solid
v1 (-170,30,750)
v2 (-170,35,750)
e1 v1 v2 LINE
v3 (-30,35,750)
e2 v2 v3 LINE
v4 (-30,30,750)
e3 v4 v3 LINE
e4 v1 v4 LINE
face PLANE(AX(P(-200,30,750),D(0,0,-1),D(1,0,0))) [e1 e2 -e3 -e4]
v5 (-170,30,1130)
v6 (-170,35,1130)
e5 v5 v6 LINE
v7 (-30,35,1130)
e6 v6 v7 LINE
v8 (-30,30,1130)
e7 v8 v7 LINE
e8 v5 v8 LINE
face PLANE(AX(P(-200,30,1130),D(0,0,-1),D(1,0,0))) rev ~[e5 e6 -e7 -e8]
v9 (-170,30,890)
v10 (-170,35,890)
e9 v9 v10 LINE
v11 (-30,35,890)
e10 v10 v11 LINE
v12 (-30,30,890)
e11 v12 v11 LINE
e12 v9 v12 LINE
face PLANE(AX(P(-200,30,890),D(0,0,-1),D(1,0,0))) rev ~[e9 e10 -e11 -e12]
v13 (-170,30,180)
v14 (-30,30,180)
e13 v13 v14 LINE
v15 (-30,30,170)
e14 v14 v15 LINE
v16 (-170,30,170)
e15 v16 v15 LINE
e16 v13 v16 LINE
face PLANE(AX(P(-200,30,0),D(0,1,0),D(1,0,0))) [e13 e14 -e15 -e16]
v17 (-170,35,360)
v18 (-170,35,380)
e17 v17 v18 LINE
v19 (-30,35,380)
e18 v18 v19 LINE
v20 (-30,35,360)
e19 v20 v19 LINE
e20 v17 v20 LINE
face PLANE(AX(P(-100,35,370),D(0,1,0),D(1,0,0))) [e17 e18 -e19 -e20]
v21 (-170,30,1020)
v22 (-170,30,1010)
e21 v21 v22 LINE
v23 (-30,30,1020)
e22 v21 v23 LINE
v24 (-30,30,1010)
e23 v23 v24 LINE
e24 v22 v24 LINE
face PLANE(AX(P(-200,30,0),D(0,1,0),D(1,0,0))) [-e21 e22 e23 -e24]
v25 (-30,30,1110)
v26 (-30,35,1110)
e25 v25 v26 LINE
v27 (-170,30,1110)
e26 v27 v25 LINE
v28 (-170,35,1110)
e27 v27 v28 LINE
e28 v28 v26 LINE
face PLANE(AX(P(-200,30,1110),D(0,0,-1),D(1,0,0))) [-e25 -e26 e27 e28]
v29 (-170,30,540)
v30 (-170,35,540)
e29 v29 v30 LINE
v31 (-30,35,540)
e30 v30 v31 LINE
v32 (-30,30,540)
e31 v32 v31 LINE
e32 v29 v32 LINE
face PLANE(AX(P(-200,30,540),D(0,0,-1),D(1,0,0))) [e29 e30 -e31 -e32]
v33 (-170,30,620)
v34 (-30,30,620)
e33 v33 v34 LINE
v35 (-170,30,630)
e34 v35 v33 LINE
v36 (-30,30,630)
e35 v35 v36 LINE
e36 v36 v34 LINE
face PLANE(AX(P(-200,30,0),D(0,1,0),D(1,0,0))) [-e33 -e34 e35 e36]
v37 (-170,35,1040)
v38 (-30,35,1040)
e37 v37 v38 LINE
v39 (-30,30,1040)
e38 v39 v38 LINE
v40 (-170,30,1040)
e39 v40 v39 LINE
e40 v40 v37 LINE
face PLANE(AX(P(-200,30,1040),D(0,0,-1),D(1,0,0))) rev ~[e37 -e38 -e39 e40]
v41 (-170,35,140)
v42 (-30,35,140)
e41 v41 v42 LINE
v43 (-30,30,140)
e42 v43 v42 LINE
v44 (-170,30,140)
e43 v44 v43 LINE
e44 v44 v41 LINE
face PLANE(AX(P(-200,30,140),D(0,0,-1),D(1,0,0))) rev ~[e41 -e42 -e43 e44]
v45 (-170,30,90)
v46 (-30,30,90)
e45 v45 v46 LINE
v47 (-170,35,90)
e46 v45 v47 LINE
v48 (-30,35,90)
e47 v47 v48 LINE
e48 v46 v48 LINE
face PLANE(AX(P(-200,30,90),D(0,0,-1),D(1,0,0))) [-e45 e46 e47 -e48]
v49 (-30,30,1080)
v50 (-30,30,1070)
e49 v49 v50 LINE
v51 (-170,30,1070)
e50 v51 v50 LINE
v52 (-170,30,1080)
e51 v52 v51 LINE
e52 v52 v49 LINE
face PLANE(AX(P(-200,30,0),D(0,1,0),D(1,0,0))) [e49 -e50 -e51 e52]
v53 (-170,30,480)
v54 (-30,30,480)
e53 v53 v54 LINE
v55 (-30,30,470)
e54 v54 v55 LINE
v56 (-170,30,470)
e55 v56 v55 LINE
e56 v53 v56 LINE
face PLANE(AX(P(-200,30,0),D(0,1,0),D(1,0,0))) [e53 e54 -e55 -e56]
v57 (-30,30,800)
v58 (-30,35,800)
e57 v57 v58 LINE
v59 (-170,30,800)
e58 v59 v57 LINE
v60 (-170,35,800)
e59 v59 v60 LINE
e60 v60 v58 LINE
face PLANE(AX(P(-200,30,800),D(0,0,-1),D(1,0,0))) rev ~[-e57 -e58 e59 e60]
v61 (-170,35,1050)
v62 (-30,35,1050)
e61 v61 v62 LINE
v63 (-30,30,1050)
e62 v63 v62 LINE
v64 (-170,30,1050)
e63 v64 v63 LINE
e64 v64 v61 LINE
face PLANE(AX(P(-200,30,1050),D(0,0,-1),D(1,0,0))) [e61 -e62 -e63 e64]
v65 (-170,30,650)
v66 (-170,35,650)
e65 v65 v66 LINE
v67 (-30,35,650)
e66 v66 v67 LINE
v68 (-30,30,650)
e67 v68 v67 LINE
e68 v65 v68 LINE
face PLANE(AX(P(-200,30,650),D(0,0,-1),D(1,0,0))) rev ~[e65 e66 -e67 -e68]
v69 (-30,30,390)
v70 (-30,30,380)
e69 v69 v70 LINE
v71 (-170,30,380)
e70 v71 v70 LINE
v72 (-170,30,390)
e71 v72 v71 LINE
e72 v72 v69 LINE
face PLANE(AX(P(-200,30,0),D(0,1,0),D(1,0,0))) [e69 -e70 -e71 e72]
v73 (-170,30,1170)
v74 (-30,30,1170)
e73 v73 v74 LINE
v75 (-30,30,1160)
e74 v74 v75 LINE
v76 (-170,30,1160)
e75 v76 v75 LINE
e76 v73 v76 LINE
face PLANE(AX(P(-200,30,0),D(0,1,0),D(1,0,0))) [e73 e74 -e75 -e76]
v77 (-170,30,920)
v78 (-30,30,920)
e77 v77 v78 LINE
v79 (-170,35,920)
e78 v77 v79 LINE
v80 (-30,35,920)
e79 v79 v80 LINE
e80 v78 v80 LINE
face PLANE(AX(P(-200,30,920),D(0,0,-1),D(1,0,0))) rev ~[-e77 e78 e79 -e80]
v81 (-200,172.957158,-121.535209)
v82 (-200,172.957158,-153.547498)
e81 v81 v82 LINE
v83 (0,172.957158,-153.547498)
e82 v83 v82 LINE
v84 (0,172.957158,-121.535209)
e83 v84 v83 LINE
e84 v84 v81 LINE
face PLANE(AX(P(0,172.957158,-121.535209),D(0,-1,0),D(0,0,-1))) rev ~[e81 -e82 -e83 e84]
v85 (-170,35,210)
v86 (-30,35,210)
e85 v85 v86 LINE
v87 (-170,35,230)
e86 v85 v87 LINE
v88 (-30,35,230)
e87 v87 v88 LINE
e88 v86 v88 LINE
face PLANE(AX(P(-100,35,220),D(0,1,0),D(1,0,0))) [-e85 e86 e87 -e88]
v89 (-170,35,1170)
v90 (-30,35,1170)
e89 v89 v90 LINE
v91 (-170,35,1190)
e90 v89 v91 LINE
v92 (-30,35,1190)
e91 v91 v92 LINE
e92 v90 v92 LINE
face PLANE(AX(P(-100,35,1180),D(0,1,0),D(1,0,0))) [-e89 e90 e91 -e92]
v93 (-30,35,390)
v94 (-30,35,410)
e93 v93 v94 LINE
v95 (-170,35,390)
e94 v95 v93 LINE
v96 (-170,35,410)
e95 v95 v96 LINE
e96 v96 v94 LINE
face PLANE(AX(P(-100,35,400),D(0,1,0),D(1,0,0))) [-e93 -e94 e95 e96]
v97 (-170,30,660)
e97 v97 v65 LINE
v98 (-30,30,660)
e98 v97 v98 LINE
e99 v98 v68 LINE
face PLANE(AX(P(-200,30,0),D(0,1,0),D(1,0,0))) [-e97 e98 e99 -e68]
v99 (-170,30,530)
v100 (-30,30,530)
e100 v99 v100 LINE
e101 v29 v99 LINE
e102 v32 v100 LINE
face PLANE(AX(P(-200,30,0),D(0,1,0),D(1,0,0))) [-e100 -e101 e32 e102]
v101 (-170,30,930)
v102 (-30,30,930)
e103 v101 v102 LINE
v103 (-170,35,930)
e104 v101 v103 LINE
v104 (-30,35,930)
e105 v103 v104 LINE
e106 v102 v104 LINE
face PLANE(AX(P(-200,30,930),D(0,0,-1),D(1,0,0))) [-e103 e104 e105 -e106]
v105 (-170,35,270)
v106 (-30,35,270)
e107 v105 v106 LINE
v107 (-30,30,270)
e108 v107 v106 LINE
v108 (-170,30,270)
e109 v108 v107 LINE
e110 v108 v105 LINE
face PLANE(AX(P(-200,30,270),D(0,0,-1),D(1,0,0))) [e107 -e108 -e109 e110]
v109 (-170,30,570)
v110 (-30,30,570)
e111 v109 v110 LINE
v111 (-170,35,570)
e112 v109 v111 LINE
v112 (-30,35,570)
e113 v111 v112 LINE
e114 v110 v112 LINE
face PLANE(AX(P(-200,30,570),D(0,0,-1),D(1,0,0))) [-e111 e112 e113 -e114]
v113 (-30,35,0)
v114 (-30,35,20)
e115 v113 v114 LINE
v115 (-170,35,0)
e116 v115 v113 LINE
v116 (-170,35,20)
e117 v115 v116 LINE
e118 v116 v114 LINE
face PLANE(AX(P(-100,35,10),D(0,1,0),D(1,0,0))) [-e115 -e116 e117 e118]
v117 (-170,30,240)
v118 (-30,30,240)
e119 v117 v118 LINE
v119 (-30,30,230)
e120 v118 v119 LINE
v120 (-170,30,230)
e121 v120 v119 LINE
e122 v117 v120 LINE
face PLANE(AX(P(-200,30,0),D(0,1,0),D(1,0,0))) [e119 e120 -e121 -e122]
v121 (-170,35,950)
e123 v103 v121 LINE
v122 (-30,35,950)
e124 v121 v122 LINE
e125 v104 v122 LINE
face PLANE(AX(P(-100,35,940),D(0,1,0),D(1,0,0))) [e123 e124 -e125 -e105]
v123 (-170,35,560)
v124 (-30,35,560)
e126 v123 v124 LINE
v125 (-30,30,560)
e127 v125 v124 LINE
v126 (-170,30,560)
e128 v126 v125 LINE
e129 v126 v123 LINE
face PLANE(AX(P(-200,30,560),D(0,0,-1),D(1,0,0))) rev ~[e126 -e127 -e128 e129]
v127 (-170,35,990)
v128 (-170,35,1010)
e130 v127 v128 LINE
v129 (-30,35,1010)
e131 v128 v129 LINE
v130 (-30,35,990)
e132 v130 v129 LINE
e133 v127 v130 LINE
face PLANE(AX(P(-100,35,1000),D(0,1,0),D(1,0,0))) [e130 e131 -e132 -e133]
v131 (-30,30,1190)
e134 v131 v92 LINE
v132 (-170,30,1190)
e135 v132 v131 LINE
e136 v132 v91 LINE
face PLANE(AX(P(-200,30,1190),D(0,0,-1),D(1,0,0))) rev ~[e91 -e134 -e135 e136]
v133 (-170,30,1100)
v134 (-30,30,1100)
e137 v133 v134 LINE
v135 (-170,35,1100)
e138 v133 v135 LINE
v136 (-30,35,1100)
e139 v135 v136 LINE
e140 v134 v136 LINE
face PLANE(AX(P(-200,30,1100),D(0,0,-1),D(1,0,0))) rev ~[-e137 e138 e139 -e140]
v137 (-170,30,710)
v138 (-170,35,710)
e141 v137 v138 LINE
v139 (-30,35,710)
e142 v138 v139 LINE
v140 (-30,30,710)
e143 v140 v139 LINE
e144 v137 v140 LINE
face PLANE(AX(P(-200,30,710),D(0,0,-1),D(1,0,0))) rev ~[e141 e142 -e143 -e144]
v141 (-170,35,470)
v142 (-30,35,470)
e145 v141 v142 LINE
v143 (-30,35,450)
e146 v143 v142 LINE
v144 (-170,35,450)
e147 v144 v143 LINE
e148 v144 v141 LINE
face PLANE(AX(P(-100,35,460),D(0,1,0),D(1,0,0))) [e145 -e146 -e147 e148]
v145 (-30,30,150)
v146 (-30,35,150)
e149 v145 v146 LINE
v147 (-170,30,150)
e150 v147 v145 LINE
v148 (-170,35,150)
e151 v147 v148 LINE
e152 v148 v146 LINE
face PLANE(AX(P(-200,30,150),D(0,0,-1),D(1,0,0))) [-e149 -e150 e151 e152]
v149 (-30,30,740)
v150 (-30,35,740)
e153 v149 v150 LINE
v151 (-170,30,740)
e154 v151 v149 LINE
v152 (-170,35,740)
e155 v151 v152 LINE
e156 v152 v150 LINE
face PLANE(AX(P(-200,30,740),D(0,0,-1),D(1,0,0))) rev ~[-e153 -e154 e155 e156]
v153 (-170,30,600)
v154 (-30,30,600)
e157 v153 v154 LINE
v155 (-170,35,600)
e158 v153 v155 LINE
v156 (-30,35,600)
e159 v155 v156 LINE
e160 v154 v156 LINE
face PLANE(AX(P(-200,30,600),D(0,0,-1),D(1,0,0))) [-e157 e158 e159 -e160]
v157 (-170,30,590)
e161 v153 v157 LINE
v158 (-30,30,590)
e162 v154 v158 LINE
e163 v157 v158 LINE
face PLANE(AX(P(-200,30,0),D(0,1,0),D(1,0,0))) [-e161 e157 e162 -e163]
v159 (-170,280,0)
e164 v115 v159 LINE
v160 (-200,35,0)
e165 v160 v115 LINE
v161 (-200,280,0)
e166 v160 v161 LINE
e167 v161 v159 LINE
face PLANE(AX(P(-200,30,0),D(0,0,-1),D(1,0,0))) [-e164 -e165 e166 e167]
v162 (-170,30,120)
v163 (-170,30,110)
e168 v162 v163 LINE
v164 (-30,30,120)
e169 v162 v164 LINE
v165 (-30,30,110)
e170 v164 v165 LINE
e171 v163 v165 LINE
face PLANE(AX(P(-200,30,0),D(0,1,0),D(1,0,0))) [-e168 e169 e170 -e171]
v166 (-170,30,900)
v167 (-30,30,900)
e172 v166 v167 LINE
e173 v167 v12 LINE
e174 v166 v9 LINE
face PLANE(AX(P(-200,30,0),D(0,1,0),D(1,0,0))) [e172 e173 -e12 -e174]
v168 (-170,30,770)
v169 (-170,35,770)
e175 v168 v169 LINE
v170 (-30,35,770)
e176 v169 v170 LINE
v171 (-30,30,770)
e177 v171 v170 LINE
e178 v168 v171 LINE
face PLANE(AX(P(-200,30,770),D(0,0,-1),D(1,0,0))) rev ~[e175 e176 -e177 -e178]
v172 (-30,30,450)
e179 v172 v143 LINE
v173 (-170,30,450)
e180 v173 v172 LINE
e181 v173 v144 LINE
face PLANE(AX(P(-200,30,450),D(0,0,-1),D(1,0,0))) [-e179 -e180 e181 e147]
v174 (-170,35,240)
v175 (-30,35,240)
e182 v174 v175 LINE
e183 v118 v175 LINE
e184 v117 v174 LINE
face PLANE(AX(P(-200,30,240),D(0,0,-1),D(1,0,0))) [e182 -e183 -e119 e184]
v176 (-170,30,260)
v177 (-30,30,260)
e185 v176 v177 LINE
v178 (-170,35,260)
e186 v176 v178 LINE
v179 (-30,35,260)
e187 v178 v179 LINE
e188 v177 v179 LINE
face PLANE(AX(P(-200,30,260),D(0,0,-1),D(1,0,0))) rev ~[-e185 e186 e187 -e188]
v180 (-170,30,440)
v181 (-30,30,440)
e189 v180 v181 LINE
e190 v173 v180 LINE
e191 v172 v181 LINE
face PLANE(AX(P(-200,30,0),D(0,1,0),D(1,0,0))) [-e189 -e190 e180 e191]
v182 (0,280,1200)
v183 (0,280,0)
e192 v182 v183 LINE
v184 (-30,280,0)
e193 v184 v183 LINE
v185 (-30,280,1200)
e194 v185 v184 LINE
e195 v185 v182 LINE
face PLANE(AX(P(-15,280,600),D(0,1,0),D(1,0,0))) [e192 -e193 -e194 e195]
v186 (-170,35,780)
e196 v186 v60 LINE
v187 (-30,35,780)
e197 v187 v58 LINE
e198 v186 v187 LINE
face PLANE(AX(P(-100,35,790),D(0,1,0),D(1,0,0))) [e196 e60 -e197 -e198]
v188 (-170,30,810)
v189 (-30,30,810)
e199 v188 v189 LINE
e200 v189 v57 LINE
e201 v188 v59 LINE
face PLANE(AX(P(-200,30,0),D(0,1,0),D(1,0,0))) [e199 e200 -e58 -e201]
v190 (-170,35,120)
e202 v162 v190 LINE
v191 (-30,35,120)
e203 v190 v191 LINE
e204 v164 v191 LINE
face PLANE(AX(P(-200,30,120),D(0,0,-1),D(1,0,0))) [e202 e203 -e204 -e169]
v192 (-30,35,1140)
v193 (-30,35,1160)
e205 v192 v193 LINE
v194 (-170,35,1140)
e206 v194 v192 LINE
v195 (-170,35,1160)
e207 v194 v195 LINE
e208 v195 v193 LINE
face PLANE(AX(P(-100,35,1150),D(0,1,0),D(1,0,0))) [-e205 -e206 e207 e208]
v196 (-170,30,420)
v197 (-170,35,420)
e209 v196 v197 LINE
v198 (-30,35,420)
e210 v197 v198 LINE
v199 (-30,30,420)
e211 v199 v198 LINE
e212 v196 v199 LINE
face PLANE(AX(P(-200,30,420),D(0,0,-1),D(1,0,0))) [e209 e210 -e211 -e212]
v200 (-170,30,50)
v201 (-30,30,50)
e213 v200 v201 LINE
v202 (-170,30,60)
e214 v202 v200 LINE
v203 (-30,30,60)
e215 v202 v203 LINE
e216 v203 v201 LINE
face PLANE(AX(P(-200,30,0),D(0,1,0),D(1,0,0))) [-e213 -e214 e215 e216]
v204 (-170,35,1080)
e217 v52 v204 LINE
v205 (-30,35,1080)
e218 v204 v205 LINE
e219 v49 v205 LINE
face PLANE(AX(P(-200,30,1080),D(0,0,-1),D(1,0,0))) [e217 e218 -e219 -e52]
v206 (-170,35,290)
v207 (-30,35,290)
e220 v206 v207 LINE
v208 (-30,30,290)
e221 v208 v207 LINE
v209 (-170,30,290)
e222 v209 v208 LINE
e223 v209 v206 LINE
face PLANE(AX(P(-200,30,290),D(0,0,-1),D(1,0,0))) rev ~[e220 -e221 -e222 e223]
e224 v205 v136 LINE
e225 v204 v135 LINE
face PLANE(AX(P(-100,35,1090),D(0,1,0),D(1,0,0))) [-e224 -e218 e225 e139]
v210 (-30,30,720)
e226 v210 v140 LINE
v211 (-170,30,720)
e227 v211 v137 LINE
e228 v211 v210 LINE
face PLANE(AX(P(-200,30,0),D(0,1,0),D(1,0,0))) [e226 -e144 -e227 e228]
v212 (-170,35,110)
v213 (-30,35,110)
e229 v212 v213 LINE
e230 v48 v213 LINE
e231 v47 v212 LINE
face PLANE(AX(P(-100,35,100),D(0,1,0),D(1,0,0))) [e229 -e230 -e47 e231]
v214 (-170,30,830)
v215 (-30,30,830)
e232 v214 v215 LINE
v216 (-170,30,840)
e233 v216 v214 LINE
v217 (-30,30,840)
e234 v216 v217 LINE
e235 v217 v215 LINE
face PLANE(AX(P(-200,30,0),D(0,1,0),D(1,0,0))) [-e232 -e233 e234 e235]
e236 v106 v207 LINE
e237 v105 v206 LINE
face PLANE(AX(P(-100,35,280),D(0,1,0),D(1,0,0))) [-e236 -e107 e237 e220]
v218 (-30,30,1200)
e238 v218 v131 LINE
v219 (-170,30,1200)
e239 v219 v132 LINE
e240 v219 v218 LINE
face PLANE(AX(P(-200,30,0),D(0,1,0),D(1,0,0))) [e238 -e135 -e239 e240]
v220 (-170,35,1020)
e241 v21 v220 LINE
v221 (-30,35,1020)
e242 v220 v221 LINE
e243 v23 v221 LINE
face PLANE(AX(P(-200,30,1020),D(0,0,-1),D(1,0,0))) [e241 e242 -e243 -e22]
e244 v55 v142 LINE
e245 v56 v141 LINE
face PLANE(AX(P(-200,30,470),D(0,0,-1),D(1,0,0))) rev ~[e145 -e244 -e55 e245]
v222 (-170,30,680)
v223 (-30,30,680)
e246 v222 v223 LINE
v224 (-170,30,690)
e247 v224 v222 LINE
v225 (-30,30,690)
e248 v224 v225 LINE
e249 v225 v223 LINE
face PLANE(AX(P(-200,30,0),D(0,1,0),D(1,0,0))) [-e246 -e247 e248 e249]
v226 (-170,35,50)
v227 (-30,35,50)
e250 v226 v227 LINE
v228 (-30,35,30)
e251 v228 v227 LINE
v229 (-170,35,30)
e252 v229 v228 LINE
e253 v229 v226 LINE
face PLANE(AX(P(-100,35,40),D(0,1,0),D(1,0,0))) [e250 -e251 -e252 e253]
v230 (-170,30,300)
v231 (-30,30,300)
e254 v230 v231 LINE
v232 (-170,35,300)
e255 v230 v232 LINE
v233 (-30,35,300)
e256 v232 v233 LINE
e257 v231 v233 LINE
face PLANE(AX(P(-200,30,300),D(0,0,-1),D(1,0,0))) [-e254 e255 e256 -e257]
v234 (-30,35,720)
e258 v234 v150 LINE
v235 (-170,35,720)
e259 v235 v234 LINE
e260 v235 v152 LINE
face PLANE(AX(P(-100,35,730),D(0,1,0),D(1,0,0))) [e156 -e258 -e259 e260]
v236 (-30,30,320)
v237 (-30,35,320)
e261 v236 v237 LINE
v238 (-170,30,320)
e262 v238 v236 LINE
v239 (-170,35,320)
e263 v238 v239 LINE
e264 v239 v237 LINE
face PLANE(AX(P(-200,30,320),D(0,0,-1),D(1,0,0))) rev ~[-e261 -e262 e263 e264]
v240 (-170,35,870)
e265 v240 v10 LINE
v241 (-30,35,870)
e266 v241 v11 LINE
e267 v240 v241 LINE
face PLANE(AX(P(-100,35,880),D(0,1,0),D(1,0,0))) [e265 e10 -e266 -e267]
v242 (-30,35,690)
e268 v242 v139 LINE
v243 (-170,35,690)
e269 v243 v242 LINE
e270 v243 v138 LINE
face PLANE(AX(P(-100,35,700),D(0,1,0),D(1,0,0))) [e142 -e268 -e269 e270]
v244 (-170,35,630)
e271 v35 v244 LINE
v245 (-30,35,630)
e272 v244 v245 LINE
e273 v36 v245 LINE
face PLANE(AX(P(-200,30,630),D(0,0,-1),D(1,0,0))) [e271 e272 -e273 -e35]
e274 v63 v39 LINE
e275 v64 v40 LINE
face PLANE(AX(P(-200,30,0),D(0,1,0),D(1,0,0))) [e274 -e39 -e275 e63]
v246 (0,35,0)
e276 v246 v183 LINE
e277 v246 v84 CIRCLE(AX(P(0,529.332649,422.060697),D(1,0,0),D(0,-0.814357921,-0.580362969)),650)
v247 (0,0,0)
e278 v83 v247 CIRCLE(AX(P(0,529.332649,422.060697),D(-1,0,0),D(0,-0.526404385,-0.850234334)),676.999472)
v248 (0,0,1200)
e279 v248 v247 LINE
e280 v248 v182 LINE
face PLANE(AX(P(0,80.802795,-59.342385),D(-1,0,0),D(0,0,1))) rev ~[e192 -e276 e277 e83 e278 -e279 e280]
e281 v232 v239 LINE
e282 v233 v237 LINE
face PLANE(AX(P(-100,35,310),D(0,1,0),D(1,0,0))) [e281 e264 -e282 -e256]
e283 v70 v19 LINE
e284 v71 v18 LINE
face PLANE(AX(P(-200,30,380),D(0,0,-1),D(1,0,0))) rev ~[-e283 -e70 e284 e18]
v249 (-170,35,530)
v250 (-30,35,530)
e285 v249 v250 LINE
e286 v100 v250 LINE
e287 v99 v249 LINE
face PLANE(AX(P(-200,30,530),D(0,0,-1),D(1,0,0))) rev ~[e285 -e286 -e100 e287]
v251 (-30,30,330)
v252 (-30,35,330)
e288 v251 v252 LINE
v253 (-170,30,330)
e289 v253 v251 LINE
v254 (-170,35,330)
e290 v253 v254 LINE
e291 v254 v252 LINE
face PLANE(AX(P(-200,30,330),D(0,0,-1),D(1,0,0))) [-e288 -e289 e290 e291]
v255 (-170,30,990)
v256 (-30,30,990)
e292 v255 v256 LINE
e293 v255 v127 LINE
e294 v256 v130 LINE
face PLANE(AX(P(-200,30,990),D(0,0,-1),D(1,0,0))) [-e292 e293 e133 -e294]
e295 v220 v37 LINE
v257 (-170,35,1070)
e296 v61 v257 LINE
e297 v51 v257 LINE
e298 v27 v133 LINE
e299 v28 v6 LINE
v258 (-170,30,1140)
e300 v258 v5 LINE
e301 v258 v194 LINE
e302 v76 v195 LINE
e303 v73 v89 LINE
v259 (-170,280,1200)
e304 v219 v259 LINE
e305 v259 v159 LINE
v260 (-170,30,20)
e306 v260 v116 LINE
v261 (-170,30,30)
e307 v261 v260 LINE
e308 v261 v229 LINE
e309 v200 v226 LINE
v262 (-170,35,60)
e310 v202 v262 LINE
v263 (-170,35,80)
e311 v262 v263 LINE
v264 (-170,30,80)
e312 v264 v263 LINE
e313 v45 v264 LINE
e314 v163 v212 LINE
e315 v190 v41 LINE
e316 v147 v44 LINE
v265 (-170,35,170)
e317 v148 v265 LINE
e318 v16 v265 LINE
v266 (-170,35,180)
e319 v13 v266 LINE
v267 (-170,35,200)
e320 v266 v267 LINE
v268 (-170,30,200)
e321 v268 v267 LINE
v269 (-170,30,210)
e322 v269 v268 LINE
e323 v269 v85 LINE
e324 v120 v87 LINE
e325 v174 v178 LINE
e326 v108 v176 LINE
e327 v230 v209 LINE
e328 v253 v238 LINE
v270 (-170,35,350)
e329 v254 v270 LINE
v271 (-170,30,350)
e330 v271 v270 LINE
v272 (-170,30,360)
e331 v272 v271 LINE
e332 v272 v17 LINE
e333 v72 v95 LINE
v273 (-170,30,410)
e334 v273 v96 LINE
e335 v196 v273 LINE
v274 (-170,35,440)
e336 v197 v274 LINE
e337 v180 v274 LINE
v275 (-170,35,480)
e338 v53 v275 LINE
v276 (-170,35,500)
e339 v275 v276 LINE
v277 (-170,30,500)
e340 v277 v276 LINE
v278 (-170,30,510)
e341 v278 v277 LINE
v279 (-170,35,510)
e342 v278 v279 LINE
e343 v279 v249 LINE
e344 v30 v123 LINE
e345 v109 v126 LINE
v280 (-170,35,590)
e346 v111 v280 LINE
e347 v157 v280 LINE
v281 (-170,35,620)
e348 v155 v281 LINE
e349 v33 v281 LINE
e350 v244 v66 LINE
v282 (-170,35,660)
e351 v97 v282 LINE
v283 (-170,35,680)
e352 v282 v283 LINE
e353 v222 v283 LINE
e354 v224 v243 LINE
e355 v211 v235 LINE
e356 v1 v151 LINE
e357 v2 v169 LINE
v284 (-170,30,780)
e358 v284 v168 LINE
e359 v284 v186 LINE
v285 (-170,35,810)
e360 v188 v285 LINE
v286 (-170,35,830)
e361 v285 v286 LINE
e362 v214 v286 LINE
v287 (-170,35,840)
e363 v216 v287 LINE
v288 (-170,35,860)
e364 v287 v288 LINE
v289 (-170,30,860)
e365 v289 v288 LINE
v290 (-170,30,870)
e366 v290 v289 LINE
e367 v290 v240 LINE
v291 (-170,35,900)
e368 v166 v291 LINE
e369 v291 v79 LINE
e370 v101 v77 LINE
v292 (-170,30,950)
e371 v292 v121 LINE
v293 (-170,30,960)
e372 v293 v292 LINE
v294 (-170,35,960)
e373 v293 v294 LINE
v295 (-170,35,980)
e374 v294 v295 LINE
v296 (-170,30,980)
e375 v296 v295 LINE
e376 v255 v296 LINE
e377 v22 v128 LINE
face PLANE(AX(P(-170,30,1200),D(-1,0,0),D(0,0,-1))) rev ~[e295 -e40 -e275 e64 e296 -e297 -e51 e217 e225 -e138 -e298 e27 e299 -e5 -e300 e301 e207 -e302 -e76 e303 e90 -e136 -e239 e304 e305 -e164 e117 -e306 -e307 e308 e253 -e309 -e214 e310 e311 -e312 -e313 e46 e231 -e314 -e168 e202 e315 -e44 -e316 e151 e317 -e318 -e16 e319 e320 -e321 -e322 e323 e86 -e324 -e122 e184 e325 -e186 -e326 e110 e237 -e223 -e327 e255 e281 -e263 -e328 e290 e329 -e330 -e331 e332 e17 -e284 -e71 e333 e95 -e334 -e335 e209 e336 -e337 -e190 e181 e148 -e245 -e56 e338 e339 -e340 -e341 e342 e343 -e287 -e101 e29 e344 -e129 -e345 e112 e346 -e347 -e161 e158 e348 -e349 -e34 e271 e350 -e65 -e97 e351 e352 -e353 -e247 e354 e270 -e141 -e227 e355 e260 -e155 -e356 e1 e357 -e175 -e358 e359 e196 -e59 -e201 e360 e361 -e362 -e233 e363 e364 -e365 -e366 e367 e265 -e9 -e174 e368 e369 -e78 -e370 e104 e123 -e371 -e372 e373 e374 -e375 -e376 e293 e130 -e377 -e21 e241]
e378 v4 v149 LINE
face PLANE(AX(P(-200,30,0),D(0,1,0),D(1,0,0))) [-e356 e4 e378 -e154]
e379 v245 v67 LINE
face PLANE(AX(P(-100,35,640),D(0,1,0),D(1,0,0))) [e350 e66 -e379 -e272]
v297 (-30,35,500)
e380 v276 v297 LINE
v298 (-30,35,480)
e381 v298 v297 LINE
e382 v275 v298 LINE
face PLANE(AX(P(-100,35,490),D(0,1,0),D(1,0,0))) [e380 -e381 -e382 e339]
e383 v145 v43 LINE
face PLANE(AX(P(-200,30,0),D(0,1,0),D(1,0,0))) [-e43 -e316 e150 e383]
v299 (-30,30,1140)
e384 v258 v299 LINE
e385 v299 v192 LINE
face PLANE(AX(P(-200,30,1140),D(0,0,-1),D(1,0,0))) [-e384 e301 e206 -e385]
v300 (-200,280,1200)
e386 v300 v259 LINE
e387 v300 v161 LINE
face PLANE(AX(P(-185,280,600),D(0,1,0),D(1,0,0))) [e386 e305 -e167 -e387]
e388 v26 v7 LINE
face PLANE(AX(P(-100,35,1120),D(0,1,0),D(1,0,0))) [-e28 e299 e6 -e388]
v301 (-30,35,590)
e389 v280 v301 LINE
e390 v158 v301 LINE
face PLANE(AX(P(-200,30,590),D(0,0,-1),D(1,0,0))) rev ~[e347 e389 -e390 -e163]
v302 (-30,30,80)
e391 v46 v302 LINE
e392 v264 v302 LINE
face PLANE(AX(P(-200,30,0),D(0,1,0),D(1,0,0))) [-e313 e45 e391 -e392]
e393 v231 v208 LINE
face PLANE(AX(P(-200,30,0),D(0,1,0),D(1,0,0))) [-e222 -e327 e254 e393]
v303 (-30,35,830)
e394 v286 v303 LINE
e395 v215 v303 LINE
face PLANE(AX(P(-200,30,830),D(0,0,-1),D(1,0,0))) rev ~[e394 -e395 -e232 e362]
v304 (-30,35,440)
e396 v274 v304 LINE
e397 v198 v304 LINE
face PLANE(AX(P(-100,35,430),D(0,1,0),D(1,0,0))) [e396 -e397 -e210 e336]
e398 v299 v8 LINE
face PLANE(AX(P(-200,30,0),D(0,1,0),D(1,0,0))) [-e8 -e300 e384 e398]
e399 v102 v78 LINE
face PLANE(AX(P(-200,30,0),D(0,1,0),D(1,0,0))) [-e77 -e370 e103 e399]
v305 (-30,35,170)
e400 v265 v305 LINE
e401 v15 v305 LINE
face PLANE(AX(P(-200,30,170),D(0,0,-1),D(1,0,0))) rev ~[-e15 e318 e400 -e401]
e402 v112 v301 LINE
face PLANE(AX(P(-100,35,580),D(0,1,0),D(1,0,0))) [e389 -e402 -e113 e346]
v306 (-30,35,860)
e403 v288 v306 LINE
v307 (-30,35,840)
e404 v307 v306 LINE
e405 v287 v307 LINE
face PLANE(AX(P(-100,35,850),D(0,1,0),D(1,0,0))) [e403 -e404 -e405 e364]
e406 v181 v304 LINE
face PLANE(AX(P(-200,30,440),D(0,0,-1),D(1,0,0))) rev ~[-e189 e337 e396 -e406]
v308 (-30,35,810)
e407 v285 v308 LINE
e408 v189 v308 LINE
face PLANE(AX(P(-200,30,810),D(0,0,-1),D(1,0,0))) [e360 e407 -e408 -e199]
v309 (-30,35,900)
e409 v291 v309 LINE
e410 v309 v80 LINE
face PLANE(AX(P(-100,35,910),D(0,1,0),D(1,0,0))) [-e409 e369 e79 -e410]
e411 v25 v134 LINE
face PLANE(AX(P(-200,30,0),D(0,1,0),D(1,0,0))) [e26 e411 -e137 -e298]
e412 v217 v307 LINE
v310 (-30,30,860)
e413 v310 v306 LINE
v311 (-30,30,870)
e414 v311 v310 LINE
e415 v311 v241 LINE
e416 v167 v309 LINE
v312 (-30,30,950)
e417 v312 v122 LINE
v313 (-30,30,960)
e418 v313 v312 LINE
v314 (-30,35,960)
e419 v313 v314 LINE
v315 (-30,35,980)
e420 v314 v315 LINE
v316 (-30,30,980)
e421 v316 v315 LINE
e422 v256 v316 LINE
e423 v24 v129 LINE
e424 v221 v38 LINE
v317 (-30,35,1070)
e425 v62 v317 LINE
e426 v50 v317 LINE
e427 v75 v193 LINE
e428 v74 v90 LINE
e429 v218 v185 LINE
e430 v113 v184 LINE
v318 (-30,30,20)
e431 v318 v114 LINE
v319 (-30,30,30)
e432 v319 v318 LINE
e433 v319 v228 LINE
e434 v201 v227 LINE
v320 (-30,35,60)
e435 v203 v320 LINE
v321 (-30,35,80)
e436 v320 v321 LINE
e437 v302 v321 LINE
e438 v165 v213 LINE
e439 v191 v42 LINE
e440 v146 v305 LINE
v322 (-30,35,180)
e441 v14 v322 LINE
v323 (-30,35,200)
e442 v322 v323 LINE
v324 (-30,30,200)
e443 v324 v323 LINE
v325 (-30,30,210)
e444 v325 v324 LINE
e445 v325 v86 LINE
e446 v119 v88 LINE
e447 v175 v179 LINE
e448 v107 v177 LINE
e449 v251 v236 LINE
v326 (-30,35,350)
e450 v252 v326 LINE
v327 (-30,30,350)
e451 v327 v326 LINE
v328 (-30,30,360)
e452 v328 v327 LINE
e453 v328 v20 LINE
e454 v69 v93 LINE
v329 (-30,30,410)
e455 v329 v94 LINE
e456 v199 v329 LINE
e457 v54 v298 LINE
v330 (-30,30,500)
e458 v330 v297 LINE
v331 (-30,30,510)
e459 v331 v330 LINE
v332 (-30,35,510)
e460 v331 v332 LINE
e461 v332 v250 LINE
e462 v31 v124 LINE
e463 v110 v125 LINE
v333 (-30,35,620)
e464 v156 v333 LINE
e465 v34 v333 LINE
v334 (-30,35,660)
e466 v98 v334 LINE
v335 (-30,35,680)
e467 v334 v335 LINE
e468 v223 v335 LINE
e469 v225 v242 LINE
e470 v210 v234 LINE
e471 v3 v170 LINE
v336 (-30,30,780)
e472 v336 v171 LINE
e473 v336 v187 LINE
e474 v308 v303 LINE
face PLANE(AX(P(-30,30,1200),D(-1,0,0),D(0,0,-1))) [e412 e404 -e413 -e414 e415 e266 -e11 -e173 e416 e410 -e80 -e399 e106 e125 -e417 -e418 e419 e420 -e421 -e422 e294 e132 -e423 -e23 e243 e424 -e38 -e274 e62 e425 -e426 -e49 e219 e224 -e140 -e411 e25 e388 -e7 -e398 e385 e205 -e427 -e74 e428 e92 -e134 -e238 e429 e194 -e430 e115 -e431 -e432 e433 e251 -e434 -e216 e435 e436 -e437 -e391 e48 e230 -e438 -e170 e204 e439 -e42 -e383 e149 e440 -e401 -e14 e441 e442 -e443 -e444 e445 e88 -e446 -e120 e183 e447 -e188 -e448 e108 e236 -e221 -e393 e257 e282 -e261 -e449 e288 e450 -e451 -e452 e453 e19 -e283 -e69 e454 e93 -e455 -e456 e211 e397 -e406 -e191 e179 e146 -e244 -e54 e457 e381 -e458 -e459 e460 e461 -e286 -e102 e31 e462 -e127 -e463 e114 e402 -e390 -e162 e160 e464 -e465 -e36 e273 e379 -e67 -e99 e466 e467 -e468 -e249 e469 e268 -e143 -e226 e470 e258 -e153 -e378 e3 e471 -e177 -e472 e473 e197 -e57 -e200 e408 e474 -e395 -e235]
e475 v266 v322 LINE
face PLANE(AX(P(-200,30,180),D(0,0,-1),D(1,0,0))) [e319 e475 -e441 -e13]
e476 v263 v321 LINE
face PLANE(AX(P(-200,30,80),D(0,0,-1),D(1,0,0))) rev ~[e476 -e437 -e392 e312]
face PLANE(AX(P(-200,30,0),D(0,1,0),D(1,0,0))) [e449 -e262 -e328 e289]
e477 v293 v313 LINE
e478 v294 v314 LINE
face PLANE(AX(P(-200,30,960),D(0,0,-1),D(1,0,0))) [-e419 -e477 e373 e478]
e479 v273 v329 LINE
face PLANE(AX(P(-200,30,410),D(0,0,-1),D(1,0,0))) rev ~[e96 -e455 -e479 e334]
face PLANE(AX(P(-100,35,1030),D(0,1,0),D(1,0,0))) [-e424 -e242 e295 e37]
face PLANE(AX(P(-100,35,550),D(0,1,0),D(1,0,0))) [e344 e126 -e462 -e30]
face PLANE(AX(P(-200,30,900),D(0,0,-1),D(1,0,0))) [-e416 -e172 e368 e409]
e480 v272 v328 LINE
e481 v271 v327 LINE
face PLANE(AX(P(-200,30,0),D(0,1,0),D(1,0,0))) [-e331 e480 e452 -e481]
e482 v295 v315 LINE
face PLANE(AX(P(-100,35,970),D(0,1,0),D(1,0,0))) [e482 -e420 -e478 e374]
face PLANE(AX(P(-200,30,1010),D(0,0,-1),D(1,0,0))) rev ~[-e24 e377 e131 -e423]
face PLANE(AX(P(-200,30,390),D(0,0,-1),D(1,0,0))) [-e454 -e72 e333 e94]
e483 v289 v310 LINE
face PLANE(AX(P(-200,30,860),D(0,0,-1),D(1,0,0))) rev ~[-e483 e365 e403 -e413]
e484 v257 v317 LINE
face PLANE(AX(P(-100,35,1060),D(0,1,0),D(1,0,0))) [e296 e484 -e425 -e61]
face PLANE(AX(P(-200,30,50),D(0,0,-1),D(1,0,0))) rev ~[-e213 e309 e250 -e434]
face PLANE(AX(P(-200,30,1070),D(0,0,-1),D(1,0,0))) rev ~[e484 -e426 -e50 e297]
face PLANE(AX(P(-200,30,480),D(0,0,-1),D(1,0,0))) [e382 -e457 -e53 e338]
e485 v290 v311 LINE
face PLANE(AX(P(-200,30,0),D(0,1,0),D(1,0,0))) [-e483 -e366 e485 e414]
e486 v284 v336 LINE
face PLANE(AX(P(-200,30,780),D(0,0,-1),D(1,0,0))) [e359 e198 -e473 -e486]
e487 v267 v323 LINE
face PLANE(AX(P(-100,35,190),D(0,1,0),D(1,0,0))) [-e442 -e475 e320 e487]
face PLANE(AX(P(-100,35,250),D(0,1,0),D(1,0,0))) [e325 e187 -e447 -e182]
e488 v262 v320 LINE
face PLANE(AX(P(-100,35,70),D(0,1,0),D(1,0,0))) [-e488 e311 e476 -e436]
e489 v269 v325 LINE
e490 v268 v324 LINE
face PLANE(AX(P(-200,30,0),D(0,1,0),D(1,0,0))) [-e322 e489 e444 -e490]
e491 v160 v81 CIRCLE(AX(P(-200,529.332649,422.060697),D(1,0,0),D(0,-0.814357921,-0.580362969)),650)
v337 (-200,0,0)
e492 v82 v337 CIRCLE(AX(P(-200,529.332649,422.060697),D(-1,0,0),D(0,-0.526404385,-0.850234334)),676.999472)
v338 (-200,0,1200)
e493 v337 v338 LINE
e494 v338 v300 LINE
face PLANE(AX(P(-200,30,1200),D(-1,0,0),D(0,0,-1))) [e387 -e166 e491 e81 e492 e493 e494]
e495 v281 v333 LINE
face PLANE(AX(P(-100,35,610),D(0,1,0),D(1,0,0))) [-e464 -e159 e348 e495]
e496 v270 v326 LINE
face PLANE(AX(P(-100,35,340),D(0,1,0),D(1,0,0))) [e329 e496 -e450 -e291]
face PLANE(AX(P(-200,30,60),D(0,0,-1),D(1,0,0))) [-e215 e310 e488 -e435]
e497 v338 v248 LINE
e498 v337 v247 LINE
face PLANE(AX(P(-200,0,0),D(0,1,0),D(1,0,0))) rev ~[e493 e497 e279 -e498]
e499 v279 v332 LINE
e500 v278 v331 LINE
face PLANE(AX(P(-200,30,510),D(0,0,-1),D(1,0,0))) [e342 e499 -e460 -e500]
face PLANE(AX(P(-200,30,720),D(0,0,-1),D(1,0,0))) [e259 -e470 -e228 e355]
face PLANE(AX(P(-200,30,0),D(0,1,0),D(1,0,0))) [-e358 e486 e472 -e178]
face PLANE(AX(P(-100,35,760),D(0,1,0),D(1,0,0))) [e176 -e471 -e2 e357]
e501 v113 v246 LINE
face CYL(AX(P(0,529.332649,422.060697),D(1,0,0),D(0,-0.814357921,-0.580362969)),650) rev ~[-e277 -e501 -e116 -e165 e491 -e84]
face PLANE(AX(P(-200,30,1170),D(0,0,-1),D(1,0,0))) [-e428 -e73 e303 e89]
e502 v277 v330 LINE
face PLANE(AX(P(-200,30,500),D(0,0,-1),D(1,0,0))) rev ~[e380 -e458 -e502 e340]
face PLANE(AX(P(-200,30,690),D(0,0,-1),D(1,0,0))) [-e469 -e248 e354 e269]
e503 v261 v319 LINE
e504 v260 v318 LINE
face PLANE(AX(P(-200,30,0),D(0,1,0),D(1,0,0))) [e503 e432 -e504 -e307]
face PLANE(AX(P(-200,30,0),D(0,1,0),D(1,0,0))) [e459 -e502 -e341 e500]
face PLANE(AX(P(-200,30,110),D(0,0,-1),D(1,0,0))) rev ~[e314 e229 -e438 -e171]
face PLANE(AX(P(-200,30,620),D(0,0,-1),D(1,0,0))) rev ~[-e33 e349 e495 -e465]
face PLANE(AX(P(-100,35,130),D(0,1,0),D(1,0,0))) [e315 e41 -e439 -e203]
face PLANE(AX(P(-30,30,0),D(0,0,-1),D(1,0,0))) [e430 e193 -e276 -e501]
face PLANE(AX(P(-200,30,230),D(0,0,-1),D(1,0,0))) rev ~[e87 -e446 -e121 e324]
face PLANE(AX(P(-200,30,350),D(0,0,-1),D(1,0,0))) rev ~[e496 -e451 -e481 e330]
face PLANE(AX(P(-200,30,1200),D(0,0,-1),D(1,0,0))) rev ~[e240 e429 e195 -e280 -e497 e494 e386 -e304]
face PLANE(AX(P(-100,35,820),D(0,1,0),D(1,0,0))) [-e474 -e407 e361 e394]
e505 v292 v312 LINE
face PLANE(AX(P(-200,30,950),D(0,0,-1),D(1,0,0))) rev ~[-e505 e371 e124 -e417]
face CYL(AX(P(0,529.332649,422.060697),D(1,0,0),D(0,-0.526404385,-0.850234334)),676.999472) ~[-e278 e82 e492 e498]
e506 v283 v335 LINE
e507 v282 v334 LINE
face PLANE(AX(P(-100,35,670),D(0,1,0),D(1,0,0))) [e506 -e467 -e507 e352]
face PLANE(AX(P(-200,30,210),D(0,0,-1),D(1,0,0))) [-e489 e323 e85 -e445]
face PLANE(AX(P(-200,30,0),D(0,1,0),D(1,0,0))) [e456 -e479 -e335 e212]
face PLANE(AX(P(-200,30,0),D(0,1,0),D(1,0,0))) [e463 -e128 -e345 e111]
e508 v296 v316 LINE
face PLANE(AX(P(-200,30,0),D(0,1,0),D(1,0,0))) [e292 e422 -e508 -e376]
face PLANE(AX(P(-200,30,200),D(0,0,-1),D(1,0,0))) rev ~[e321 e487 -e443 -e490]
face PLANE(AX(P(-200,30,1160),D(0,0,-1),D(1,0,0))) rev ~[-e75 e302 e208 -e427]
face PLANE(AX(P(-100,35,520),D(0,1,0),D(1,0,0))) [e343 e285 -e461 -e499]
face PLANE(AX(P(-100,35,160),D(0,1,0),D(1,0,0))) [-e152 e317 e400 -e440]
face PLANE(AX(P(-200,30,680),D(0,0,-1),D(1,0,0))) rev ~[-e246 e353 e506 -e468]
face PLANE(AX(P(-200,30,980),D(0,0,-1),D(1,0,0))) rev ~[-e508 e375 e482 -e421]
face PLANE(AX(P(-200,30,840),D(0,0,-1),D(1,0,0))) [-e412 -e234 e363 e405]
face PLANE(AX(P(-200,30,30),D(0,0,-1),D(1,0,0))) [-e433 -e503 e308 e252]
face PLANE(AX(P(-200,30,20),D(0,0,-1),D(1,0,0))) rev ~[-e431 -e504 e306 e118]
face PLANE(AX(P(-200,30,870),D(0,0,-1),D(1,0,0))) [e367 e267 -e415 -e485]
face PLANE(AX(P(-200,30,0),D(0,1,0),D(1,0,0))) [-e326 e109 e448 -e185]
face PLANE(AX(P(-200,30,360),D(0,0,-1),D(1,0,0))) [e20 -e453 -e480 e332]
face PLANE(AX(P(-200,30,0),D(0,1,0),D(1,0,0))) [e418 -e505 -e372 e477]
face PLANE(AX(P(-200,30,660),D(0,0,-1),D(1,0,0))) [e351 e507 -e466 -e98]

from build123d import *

# Parameters (mm, degrees)
SKETCH1_W           = 200
SKETCH1_H           = 30
BOSS_EXTRUDE1_DEPTH = 1200
SKETCH2_W           = 200
SKETCH2_H           = 20
BOSS_EXTRUDE2_DEPTH = 5
BOSS_EXTRUDE3_DEPTH = 200
SKETCH5_W           = 30
SKETCH5_H           = 1200
BOSS_EXTRUDE5_DEPTH = 250


with BuildPart() as part:
    # Sketch1 → Boss-Extrude1 (new body)
    with BuildSketch(Plane.XY):
        with Locations((-100, 15)):
            Rectangle(SKETCH1_W, SKETCH1_H)
    extrude(amount=BOSS_EXTRUDE1_DEPTH)

    # Sketch2 → Boss-Extrude2 (add)
    with BuildSketch(Plane(origin=(0, 30, 0), x_dir=(1, 0, 0), z_dir=(0, 1, 0))):
        with Locations((-100, -10)):
            Rectangle(SKETCH2_W, SKETCH2_H)
        with Locations((-100, -40)):
            Rectangle(SKETCH2_W, SKETCH2_H)
        with Locations((-100, -70)):
            Rectangle(SKETCH2_W, SKETCH2_H)
        with Locations((-100, -100)):
            Rectangle(SKETCH2_W, SKETCH2_H)
        with Locations((-100, -130)):
            Rectangle(SKETCH2_W, SKETCH2_H)
        with Locations((-100, -160)):
            Rectangle(SKETCH2_W, SKETCH2_H)
        with Locations((-100, -190)):
            Rectangle(SKETCH2_W, SKETCH2_H)
        with Locations((-100, -220)):
            Rectangle(SKETCH2_W, SKETCH2_H)
        with Locations((-100, -250)):
            Rectangle(SKETCH2_W, SKETCH2_H)
        with Locations((-100, -280)):
            Rectangle(SKETCH2_W, SKETCH2_H)
        with Locations((-100, -310)):
            Rectangle(SKETCH2_W, SKETCH2_H)
        with Locations((-100, -340)):
            Rectangle(SKETCH2_W, SKETCH2_H)
        with Locations((-100, -370)):
            Rectangle(SKETCH2_W, SKETCH2_H)
        with Locations((-100, -400)):
            Rectangle(SKETCH2_W, SKETCH2_H)
        with Locations((-100, -430)):
            Rectangle(SKETCH2_W, SKETCH2_H)
        with Locations((-100, -460)):
            Rectangle(SKETCH2_W, SKETCH2_H)
        with Locations((-100, -490)):
            Rectangle(SKETCH2_W, SKETCH2_H)
        with Locations((-100, -520)):
            Rectangle(SKETCH2_W, SKETCH2_H)
        with Locations((-100, -550)):
            Rectangle(SKETCH2_W, SKETCH2_H)
        with Locations((-100, -580)):
            Rectangle(SKETCH2_W, SKETCH2_H)
        with Locations((-100, -610)):
            Rectangle(SKETCH2_W, SKETCH2_H)
        with Locations((-100, -640)):
            Rectangle(SKETCH2_W, SKETCH2_H)
        with Locations((-100, -670)):
            Rectangle(SKETCH2_W, SKETCH2_H)
        with Locations((-100, -700)):
            Rectangle(SKETCH2_W, SKETCH2_H)
        with Locations((-100, -730)):
            Rectangle(SKETCH2_W, SKETCH2_H)
        with Locations((-100, -760)):
            Rectangle(SKETCH2_W, SKETCH2_H)
        with Locations((-100, -790)):
            Rectangle(SKETCH2_W, SKETCH2_H)
        with Locations((-100, -820)):
            Rectangle(SKETCH2_W, SKETCH2_H)
        with Locations((-100, -850)):
            Rectangle(SKETCH2_W, SKETCH2_H)
        with Locations((-100, -880)):
            Rectangle(SKETCH2_W, SKETCH2_H)
        with Locations((-100, -910)):
            Rectangle(SKETCH2_W, SKETCH2_H)
        with Locations((-100, -940)):
            Rectangle(SKETCH2_W, SKETCH2_H)
        with Locations((-100, -970)):
            Rectangle(SKETCH2_W, SKETCH2_H)
        with Locations((-100, -1000)):
            Rectangle(SKETCH2_W, SKETCH2_H)
        with Locations((-100, -1030)):
            Rectangle(SKETCH2_W, SKETCH2_H)
        with Locations((-100, -1060)):
            Rectangle(SKETCH2_W, SKETCH2_H)
        with Locations((-100, -1090)):
            Rectangle(SKETCH2_W, SKETCH2_H)
        with Locations((-100, -1120)):
            Rectangle(SKETCH2_W, SKETCH2_H)
        with Locations((-100, -1150)):
            Rectangle(SKETCH2_W, SKETCH2_H)
        with Locations((-100, -1180)):
            Rectangle(SKETCH2_W, SKETCH2_H)
    extrude(amount=BOSS_EXTRUDE2_DEPTH)

    # Sketch3 → Boss-Extrude3 (add)
    with BuildSketch(Plane(origin=(0, 0, 0), x_dir=(0, 0, -1), z_dir=(1, 0, 0))):
        with BuildLine():
            Line((121.535209025, 172.957157936), (153.547498251, 172.957157936))
            ThreePointArc((153.547498251, 172.957157936), (84.214276957, 79.873044696), (0, 0))
            Line((0, 0), (-44.824767416, 0))
            ThreePointArc((-44.824767416, 0), (46.406337039, 78.734560026), (121.535209025, 172.957157936))
        make_face()
    extrude(amount=-BOSS_EXTRUDE3_DEPTH)

    # Sketch5 → Boss-Extrude5 (add)
    with BuildSketch(Plane(origin=(0, 30, 0), x_dir=(1, 0, 0), z_dir=(0, 1, 0))):
        with Locations((-185, -600)):
            Rectangle(SKETCH5_W, SKETCH5_H)
        with Locations((-15, -600)):
            Rectangle(SKETCH5_W, SKETCH5_H)
    extrude(amount=BOSS_EXTRUDE5_DEPTH)


solid = part.part
